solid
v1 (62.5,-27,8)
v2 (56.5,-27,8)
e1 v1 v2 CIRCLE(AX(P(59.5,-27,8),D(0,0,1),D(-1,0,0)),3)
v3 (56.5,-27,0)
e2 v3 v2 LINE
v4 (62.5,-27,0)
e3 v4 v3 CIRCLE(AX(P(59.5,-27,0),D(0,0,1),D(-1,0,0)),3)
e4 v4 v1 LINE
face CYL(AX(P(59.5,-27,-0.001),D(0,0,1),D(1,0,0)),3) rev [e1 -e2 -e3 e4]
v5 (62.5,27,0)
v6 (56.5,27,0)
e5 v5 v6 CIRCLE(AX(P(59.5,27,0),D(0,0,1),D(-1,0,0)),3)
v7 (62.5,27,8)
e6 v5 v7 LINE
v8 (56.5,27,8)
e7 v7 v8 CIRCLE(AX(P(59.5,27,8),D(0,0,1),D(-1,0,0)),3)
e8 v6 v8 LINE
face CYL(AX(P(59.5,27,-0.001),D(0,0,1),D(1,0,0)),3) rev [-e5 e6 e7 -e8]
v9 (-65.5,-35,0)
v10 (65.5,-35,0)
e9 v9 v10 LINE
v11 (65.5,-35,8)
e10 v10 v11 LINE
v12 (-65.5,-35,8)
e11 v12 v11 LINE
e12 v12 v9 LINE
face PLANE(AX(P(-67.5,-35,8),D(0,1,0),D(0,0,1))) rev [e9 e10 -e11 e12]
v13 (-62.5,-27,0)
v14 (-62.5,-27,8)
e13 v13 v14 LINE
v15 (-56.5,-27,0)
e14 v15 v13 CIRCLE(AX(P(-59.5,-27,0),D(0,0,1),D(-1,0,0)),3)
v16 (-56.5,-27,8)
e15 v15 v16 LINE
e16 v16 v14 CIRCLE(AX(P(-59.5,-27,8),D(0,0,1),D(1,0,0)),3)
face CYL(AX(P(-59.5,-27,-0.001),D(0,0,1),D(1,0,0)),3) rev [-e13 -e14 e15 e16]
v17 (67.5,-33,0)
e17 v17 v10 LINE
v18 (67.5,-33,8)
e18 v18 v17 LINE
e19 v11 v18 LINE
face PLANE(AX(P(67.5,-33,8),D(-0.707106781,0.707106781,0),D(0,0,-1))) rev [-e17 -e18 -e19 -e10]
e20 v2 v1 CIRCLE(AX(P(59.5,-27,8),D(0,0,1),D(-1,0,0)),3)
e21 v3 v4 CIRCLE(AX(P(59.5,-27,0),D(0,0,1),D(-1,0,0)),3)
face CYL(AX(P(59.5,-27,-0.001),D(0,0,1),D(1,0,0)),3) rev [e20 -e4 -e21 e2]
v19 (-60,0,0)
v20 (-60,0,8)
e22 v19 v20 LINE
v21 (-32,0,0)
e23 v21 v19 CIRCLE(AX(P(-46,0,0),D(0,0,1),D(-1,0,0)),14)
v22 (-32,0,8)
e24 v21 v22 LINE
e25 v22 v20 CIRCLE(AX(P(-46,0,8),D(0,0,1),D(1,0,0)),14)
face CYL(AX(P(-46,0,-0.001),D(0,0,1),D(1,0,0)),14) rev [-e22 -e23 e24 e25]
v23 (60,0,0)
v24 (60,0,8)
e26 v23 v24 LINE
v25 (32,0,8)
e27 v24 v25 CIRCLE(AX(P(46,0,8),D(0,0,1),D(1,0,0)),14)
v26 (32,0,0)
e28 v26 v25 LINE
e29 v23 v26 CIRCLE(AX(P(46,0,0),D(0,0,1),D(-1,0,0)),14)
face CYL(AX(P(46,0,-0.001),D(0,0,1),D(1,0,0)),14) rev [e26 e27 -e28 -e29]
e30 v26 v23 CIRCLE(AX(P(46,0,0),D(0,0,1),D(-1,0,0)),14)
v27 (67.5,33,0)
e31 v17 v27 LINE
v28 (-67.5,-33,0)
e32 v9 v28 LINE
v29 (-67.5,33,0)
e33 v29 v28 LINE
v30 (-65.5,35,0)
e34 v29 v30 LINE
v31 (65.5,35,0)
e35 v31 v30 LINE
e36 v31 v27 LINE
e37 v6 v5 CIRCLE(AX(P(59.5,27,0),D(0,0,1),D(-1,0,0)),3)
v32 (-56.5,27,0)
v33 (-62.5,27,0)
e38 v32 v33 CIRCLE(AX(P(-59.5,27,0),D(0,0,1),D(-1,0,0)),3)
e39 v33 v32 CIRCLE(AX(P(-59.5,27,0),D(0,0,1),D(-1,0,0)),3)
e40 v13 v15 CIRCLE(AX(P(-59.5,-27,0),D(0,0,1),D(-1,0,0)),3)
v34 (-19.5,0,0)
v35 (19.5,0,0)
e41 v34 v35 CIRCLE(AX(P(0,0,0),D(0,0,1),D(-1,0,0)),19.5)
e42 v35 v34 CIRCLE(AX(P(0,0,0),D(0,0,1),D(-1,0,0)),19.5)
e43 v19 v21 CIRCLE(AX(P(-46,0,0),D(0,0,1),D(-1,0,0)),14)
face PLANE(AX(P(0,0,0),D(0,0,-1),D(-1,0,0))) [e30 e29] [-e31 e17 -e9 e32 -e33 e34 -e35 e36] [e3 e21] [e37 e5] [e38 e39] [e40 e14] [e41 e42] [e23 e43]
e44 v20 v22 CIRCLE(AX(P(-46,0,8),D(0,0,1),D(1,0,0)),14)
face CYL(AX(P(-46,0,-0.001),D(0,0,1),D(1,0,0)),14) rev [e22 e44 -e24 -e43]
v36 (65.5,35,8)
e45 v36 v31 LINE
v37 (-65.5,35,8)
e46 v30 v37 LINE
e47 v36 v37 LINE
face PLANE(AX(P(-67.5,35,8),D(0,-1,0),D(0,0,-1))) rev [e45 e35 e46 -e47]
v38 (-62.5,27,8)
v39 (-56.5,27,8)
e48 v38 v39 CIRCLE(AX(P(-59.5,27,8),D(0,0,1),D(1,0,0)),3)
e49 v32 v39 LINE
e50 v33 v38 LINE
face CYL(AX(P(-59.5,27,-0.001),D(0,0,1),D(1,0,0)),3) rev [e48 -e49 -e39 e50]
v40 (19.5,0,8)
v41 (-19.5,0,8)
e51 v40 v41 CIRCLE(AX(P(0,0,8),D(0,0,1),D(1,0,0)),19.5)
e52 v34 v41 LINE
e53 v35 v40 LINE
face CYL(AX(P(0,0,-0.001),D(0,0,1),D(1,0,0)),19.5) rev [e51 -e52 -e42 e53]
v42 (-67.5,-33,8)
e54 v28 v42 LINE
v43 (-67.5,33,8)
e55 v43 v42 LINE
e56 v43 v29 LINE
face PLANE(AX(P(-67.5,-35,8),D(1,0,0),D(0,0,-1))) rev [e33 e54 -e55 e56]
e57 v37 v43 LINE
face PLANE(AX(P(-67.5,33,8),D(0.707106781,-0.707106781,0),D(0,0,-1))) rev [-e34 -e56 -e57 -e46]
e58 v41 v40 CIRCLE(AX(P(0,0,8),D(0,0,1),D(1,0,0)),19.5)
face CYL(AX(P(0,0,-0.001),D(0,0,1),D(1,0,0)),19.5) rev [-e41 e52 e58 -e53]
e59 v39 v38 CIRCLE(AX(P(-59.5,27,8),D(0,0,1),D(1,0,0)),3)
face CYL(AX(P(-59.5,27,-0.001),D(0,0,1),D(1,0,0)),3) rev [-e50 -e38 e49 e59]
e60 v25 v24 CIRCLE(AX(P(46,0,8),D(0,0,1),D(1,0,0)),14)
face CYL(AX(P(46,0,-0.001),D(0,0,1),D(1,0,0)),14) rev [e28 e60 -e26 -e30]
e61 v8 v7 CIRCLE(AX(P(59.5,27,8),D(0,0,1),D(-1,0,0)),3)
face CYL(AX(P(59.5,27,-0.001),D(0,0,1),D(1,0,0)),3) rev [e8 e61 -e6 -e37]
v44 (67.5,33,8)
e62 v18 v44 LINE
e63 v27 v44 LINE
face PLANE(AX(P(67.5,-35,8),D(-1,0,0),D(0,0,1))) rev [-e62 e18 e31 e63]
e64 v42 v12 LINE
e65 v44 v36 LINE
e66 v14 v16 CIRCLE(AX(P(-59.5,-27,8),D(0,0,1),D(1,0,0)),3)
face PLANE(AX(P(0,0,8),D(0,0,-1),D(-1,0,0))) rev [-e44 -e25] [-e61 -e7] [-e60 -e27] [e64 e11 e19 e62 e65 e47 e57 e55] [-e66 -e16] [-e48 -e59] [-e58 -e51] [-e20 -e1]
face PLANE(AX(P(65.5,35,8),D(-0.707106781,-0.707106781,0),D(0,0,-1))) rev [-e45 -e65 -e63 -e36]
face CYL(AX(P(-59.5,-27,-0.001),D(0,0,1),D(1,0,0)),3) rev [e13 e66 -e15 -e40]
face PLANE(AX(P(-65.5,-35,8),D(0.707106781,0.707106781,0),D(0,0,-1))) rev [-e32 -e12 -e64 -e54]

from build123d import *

# Parameters (mm, degrees)
SKETCH_1_W          = 135
SKETCH_1_H          = 70
EXTRUDE_1_DEPTH     = 8
CUT_EXTRUDE_1_REACH = 78.454
SKETCH_2_R          = 19.5
CUT_EXTRUDE_2_REACH = 78.454
SKETCH_3_R          = 14
CUT_EXTRUDE_3_REACH = 78.454
SKETCH_4_R          = 3
CHAMFER_1_SIZE      = 2


with BuildPart() as part:
    # 草图1 → 凸台-拉伸1 (new body)
    with BuildSketch(Plane.XY):
        Rectangle(SKETCH_1_W, SKETCH_1_H)
    extrude(amount=EXTRUDE_1_DEPTH)

    # 草图2 → 切除-拉伸1 (cut, up to next)
    with BuildSketch(Plane.XY.offset(8), mode=Mode.PRIVATE) as cut_extrude_1_sk1:
        Circle(SKETCH_2_R)
    cut_extrude_1_tool1 = extrude(cut_extrude_1_sk1.sketch, amount=-CUT_EXTRUDE_1_REACH, mode=Mode.PRIVATE) & part.part
    add(cut_extrude_1_tool1.solids().sort_by_distance((0, 0, 8))[0], mode=Mode.SUBTRACT)

    # 草图3 → 切除-拉伸2 (cut, up to next)
    with BuildSketch(Plane.XY.offset(8), mode=Mode.PRIVATE) as cut_extrude_2_sk1:
        with Locations((46, 0)):
            Circle(SKETCH_3_R)
    cut_extrude_2_tool1 = extrude(cut_extrude_2_sk1.sketch, amount=-CUT_EXTRUDE_2_REACH, mode=Mode.PRIVATE) & part.part
    # 草图3 → 切除-拉伸2 (cut, up to next)
    with BuildSketch(Plane.XY.offset(8), mode=Mode.PRIVATE) as cut_extrude_2_sk2:
        with Locations((-46, 0)):
            Circle(SKETCH_3_R)
    cut_extrude_2_tool2 = extrude(cut_extrude_2_sk2.sketch, amount=-CUT_EXTRUDE_2_REACH, mode=Mode.PRIVATE) & part.part
    add(cut_extrude_2_tool1.solids().sort_by_distance((46, 0, 8))[0], mode=Mode.SUBTRACT)
    add(cut_extrude_2_tool2.solids().sort_by_distance((-46, 0, 8))[0], mode=Mode.SUBTRACT)

    # 草图4 → 切除-拉伸3 (cut, up to next)
    with BuildSketch(Plane.XY.offset(8), mode=Mode.PRIVATE) as cut_extrude_3_sk1:
        with Locations((-59.5, 27)):
            Circle(SKETCH_4_R)
    cut_extrude_3_tool1 = extrude(cut_extrude_3_sk1.sketch, amount=-CUT_EXTRUDE_3_REACH, mode=Mode.PRIVATE) & part.part
    # 草图4 → 切除-拉伸3 (cut, up to next)
    with BuildSketch(Plane.XY.offset(8), mode=Mode.PRIVATE) as cut_extrude_3_sk2:
        with Locations((-59.5, -27)):
            Circle(SKETCH_4_R)
    cut_extrude_3_tool2 = extrude(cut_extrude_3_sk2.sketch, amount=-CUT_EXTRUDE_3_REACH, mode=Mode.PRIVATE) & part.part
    # 草图4 → 切除-拉伸3 (cut, up to next)
    with BuildSketch(Plane.XY.offset(8), mode=Mode.PRIVATE) as cut_extrude_3_sk3:
        with Locations(Location((59.5, -27, 0), (0, 0, 180))):
            Circle(SKETCH_4_R)
    cut_extrude_3_tool3 = extrude(cut_extrude_3_sk3.sketch, amount=-CUT_EXTRUDE_3_REACH, mode=Mode.PRIVATE) & part.part
    # 草图4 → 切除-拉伸3 (cut, up to next)
    with BuildSketch(Plane.XY.offset(8), mode=Mode.PRIVATE) as cut_extrude_3_sk4:
        with Locations(Location((59.5, 27, 0), (0, 0, 180))):
            Circle(SKETCH_4_R)
    cut_extrude_3_tool4 = extrude(cut_extrude_3_sk4.sketch, amount=-CUT_EXTRUDE_3_REACH, mode=Mode.PRIVATE) & part.part
    add(cut_extrude_3_tool1.solids().sort_by_distance((-59.5, 27, 8))[0], mode=Mode.SUBTRACT)
    add(cut_extrude_3_tool2.solids().sort_by_distance((-59.5, -27, 8))[0], mode=Mode.SUBTRACT)
    add(cut_extrude_3_tool3.solids().sort_by_distance((59.5, -27, 8))[0], mode=Mode.SUBTRACT)
    add(cut_extrude_3_tool4.solids().sort_by_distance((59.5, 27, 8))[0], mode=Mode.SUBTRACT)

    # 倒角1
    chamfer_1_edges = [part.edges().sort_by_distance(p)[0] for p in [
        (67.5, -35, 4),
        (-67.5, -35, 4),
        (-67.5, 35, 4),
        (67.5, 35, 4),
    ]]
    chamfer(chamfer_1_edges, length=CHAMFER_1_SIZE)


solid = part.part
